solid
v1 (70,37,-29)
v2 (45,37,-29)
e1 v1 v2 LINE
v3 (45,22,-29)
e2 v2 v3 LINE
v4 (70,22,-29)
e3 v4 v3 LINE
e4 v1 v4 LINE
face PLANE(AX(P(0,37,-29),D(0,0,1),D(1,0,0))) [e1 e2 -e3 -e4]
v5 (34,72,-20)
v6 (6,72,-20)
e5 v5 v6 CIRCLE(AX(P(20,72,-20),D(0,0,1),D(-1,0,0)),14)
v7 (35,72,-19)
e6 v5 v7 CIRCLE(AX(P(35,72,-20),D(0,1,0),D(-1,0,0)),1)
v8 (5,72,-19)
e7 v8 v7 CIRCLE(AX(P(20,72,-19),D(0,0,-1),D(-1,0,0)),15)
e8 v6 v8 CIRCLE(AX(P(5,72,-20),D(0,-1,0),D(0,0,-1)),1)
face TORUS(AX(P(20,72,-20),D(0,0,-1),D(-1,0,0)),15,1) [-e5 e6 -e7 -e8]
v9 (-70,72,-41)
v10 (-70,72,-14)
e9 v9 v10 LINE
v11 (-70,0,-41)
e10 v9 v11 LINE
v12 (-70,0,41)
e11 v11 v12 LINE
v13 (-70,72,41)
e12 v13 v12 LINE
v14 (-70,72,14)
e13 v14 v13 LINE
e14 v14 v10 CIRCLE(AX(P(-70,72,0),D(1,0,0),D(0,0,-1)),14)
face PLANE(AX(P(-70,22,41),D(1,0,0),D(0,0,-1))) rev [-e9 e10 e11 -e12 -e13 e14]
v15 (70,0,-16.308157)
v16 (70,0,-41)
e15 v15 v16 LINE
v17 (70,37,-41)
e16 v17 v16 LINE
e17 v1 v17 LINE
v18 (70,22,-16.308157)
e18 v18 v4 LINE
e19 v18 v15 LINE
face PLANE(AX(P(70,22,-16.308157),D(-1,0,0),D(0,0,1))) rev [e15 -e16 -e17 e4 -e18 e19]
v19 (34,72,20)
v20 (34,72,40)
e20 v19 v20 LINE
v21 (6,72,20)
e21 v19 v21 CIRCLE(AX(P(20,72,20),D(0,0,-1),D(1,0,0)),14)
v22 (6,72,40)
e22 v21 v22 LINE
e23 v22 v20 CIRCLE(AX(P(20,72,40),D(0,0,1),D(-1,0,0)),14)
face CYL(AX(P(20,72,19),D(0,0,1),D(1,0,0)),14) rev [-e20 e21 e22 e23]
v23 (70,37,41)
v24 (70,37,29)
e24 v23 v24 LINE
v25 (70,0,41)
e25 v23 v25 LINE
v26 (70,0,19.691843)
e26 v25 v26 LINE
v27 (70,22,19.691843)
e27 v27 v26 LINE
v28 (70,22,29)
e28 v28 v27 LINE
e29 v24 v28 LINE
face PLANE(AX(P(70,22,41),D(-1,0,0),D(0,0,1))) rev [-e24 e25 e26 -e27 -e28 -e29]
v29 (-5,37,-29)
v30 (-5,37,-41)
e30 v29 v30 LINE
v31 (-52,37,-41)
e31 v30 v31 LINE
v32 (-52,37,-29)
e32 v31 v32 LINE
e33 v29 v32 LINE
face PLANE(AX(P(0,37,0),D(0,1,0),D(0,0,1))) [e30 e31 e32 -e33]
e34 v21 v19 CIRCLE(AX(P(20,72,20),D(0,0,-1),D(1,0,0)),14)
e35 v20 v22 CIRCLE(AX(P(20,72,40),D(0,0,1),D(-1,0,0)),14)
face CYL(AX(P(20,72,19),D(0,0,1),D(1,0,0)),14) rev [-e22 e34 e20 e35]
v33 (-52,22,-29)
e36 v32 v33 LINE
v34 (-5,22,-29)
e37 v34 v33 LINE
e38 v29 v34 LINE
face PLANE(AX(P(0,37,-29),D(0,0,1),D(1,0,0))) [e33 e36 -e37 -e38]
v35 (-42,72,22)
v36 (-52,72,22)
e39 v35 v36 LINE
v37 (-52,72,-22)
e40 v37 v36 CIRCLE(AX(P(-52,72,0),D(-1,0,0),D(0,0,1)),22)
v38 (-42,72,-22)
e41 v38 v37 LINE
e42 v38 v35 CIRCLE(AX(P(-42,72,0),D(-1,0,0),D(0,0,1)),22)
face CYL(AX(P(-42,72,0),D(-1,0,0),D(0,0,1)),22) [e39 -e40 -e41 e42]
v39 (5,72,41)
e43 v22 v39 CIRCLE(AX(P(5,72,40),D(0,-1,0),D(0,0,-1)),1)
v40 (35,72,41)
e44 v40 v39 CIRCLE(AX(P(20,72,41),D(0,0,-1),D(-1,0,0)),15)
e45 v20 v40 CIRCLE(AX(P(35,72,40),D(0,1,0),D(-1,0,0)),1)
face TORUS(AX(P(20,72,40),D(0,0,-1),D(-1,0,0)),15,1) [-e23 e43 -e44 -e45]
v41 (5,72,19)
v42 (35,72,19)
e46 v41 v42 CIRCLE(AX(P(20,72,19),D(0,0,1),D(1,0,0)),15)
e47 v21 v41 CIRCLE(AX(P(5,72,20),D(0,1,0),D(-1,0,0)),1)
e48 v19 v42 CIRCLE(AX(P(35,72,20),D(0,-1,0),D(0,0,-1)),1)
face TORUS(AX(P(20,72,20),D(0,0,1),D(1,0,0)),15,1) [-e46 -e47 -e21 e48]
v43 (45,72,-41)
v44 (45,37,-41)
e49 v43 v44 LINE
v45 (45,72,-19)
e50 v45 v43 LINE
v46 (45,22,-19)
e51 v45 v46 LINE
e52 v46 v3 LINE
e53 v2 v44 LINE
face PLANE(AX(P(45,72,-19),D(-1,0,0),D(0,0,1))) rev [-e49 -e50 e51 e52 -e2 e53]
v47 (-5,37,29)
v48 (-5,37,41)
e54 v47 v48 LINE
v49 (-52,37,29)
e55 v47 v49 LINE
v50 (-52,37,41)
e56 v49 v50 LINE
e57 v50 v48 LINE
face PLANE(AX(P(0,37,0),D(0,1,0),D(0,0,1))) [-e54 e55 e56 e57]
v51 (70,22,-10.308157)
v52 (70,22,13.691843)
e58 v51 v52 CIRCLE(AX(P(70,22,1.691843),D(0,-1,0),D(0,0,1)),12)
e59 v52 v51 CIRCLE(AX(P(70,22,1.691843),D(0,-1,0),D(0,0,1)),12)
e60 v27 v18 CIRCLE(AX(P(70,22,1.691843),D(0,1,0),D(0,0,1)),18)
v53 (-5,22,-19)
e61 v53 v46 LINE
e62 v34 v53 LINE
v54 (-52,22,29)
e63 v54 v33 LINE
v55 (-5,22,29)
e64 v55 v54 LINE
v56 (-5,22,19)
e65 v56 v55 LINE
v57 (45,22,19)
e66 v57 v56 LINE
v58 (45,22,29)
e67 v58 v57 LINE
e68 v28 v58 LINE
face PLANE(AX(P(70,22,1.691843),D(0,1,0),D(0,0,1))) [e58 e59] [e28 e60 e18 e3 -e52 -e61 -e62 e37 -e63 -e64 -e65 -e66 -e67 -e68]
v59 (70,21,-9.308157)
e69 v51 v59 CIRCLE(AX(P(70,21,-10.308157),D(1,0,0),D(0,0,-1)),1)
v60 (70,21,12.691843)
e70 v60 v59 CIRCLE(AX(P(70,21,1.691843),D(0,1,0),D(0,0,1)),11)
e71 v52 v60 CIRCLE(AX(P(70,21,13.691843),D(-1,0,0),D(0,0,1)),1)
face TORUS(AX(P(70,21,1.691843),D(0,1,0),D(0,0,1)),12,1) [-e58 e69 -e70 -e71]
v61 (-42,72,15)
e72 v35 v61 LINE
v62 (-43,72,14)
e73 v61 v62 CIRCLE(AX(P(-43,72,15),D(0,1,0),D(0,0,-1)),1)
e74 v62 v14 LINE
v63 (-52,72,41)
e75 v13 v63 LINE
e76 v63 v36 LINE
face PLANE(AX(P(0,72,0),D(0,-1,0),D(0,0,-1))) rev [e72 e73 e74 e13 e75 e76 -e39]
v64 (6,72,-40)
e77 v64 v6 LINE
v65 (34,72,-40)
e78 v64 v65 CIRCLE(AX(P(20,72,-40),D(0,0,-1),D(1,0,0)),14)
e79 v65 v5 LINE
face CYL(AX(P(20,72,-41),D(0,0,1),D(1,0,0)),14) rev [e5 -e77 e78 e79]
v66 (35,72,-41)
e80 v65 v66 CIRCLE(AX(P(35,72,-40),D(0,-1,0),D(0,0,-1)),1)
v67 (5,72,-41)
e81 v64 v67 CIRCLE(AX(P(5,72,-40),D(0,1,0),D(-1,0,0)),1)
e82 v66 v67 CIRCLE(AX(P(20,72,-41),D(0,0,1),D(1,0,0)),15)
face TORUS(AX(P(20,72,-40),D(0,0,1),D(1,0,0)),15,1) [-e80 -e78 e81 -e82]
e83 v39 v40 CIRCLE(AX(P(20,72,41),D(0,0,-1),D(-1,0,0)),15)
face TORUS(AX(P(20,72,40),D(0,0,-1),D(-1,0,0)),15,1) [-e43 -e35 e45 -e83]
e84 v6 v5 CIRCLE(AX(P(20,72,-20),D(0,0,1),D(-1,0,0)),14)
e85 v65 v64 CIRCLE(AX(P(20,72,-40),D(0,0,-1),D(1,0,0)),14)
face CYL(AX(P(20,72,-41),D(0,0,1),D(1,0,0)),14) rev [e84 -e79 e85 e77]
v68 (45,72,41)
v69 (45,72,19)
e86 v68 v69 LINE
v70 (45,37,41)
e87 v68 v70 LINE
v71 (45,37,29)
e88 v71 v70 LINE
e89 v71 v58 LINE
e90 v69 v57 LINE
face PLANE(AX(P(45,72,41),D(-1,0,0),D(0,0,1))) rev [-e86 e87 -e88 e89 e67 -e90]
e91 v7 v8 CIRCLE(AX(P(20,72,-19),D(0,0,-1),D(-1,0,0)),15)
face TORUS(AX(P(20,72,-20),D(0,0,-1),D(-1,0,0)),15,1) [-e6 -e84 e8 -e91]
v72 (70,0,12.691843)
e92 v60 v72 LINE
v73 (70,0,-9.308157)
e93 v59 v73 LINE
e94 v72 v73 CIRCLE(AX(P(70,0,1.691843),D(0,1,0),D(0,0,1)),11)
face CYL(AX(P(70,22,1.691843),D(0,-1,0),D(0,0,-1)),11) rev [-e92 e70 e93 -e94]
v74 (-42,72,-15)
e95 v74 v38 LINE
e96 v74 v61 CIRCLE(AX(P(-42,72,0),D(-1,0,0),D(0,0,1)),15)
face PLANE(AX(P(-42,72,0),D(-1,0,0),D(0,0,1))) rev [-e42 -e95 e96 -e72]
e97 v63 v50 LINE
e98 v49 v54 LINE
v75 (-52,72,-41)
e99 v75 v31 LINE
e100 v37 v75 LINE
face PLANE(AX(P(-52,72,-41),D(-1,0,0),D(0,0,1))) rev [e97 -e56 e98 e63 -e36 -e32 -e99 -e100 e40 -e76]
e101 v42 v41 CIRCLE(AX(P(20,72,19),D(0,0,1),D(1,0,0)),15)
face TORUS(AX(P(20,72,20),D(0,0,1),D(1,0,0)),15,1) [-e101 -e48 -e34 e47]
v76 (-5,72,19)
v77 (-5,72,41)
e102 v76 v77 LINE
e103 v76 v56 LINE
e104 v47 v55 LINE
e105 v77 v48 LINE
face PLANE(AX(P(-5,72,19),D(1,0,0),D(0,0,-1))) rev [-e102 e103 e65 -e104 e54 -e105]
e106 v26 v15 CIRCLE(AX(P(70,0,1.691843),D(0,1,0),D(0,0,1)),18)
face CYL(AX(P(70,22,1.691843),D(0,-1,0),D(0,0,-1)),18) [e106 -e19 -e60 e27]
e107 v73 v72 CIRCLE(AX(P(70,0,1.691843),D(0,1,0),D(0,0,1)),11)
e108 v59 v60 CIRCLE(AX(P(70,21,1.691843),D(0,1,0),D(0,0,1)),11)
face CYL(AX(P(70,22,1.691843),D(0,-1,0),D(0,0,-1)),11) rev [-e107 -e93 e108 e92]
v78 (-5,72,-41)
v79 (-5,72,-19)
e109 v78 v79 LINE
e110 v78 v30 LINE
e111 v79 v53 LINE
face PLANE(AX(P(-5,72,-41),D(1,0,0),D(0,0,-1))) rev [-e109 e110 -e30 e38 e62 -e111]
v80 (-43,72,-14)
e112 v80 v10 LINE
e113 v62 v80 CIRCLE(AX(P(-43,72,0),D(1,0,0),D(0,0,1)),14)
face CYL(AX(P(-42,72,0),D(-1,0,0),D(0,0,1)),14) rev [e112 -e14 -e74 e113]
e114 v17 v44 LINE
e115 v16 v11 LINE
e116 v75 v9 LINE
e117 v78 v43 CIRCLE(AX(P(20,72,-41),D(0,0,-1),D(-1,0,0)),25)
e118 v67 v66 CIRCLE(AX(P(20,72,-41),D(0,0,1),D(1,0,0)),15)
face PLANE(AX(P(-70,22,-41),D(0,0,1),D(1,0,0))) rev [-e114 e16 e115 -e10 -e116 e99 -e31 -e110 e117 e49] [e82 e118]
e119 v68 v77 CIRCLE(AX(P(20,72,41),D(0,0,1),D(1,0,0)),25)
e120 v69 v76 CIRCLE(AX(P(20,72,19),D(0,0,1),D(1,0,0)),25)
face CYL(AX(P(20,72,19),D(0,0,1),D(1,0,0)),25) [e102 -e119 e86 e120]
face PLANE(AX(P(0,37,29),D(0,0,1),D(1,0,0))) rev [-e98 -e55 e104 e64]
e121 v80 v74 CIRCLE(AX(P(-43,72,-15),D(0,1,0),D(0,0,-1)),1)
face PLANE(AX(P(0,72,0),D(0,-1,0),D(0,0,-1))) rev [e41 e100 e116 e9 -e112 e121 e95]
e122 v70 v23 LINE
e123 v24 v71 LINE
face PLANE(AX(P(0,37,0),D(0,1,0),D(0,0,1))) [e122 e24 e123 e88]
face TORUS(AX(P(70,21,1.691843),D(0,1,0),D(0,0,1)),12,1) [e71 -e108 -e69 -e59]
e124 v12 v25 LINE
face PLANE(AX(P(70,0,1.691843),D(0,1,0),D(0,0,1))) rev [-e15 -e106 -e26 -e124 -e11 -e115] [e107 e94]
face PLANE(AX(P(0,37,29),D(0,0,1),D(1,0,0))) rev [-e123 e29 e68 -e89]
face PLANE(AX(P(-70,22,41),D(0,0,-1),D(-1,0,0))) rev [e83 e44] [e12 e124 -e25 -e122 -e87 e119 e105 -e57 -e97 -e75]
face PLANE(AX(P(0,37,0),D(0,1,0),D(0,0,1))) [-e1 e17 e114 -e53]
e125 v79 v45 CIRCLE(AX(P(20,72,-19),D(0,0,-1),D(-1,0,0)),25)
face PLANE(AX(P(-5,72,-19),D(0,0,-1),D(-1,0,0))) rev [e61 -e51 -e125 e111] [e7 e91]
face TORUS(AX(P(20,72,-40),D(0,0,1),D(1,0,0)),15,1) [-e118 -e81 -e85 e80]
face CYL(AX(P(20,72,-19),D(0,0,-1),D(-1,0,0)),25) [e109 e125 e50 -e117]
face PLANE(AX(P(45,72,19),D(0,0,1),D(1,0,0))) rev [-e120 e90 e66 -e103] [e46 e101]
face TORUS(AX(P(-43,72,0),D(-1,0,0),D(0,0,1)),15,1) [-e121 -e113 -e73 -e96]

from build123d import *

# Parameters (mm, degrees)
BASE_BLOCK_SKETCH_R     = 11
BASE_BLOCK_DEPTH        = 22
SIDE_WALLS_SKETCH_W     = 25
SIDE_WALLS_SKETCH_H     = 12
SIDE_WALLS_SKETCH_W_2   = 47
SIDE_WALLS_DEPTH        = 15
UPRIGHTS_SKETCH_W       = 50
UPRIGHTS_SKETCH_H       = 22
UPRIGHTS_SKETCH_W_2     = 18
UPRIGHTS_SKETCH_H_2     = 82
UPRIGHTS_DEPTH          = 50
PIVOT_LUGS_SKETCH_R     = 14
PIVOT_LUGS_DEPTH        = 22
LUG_BORE_SKETCH_R       = 14
LUG_BORE_THROUGH_DEPTH  = 82
LUG_START               = -22
LUG_INFILL_DEPTH        = 22
SADDLE_BLOCK_DEPTH      = 28
BASE_EDGE_FILLET_R1_R   = 1
LUG_EDGE_FILLETS_R1_R   = 1
SADDLE_START            = -22
SADDLE_CRADLE_CUT_DEPTH = 22


with BuildPart() as part:
    # Base Block Sketch → Base Block (new body)
    with BuildSketch(Plane(origin=(0, 0, 0), x_dir=(1, 0, 0), z_dir=(0, 1, 0))):
        with BuildLine():
            Line((70, 16.3081571), (70, 41))
            Line((70, 41), (-70, 41))
            Line((-70, 41), (-70, -41))
            Line((-70, -41), (70, -41))
            Line((70, -41), (70, -19.6918429))
            ThreePointArc((70, -19.6918429), (88, -1.6918429), (70, 16.3081571))
        make_face()
        with Locations(Location((70, -1.6918429, 0), (0, 0, 270))):
            Circle(BASE_BLOCK_SKETCH_R, mode=Mode.SUBTRACT)
    extrude(amount=BASE_BLOCK_DEPTH)

    # Side Walls Sketch → Side Walls (add)
    with BuildSketch(Plane(origin=(0, 22, 0), x_dir=(1, 0, 0), z_dir=(0, 1, 0))):
        with Locations((57.5, 35)):
            Rectangle(SIDE_WALLS_SKETCH_W, SIDE_WALLS_SKETCH_H)
        with Locations((-28.5, 35)):
            Rectangle(SIDE_WALLS_SKETCH_W_2, SIDE_WALLS_SKETCH_H)
        with Locations((-28.5, -35)):
            Rectangle(SIDE_WALLS_SKETCH_W_2, SIDE_WALLS_SKETCH_H)
        with Locations((57.5, -35)):
            Rectangle(SIDE_WALLS_SKETCH_W, SIDE_WALLS_SKETCH_H)
    extrude(amount=SIDE_WALLS_DEPTH)

    # Uprights Sketch → Uprights (add)
    with BuildSketch(Plane(origin=(0, 22, 0), x_dir=(1, 0, 0), z_dir=(0, 1, 0))):
        with Locations((20, 30)):
            Rectangle(UPRIGHTS_SKETCH_W, UPRIGHTS_SKETCH_H)
        with Locations((20, -30)):
            Rectangle(UPRIGHTS_SKETCH_W, UPRIGHTS_SKETCH_H)
        with Locations((-61, 0)):
            Rectangle(UPRIGHTS_SKETCH_W_2, UPRIGHTS_SKETCH_H_2)
    extrude(amount=UPRIGHTS_DEPTH)

    # Pivot Lugs Sketch → Pivot Lugs (add)
    with BuildSketch(Plane.XY.offset(41)):
        with BuildLine():
            Line((-5, 72), (-5, 37))
            Line((-5, 37), (45, 37))
            Line((45, 37), (45, 72))
            ThreePointArc((45, 72), (20, 97), (-5, 72))
        make_face()
        with Locations((20, 72)):
            Circle(PIVOT_LUGS_SKETCH_R, mode=Mode.SUBTRACT)
    extrude(amount=-PIVOT_LUGS_DEPTH)

    # Lug Bore Sketch → Lug Bore Through (cut)
    with BuildSketch(Plane.XY.offset(41)):
        with Locations((20, 72)):
            Circle(LUG_BORE_SKETCH_R)
    extrude(amount=-LUG_BORE_THROUGH_DEPTH, mode=Mode.SUBTRACT)

    # Lug Infill Sketch → Lug Infill (add)
    with BuildSketch(Plane(origin=(0, 0, -41), x_dir=(-1, 0, 0), z_dir=(0, 0, -1)).offset(LUG_START)):
        with BuildLine():
            Line((-34, 72), (-45, 72))
            ThreePointArc((-45, 72), (-20, 97), (5, 72))
            Line((5, 72), (-6, 72))
            ThreePointArc((-6, 72), (-20, 86), (-34, 72))
        make_face()
    extrude(amount=LUG_INFILL_DEPTH)

    # Saddle Block Sketch → Saddle Block (add)
    with BuildSketch(Plane.ZY.offset(70)):
        with BuildLine():
            Line((-14, 72), (-22, 72))
            ThreePointArc((-22, 72), (0, 50), (22, 72))
            Line((22, 72), (14, 72))
            ThreePointArc((14, 72), (0, 58), (-14, 72))
        make_face()
    extrude(amount=-SADDLE_BLOCK_DEPTH)

    # Base Edge Fillet R1
    base_edge_fillet_r1_edges = [part.edges().sort_by_distance(p)[0] for p in [
        (70, 22, -9.3081571),
    ]]
    fillet(base_edge_fillet_r1_edges, radius=BASE_EDGE_FILLET_R1_R)

    # Lug Edge Fillets R1
    lug_edge_fillets_r1_edges = [part.edges().sort_by_distance(p)[0] for p in [
        (6, 72, 41),
        (6, 72, 19),
        (34, 72, -41),
        (34, 72, -19),
        (-42, 58, 0),
    ]]
    fillet(lug_edge_fillets_r1_edges, radius=LUG_EDGE_FILLETS_R1_R)

    # Saddle Cradle Sketch → Saddle Cradle Cut (cut)
    with BuildSketch(Plane(origin=(-52, 0, 0), x_dir=(0, 0, -1), z_dir=(1, 0, 0)).offset(SADDLE_START)):
        with BuildLine():
            Line((-14, 72), (14, 72))
            ThreePointArc((14, 72), (0, 58), (-14, 72))
        make_face()
    extrude(amount=SADDLE_CRADLE_CUT_DEPTH, mode=Mode.SUBTRACT)


solid = part.part
